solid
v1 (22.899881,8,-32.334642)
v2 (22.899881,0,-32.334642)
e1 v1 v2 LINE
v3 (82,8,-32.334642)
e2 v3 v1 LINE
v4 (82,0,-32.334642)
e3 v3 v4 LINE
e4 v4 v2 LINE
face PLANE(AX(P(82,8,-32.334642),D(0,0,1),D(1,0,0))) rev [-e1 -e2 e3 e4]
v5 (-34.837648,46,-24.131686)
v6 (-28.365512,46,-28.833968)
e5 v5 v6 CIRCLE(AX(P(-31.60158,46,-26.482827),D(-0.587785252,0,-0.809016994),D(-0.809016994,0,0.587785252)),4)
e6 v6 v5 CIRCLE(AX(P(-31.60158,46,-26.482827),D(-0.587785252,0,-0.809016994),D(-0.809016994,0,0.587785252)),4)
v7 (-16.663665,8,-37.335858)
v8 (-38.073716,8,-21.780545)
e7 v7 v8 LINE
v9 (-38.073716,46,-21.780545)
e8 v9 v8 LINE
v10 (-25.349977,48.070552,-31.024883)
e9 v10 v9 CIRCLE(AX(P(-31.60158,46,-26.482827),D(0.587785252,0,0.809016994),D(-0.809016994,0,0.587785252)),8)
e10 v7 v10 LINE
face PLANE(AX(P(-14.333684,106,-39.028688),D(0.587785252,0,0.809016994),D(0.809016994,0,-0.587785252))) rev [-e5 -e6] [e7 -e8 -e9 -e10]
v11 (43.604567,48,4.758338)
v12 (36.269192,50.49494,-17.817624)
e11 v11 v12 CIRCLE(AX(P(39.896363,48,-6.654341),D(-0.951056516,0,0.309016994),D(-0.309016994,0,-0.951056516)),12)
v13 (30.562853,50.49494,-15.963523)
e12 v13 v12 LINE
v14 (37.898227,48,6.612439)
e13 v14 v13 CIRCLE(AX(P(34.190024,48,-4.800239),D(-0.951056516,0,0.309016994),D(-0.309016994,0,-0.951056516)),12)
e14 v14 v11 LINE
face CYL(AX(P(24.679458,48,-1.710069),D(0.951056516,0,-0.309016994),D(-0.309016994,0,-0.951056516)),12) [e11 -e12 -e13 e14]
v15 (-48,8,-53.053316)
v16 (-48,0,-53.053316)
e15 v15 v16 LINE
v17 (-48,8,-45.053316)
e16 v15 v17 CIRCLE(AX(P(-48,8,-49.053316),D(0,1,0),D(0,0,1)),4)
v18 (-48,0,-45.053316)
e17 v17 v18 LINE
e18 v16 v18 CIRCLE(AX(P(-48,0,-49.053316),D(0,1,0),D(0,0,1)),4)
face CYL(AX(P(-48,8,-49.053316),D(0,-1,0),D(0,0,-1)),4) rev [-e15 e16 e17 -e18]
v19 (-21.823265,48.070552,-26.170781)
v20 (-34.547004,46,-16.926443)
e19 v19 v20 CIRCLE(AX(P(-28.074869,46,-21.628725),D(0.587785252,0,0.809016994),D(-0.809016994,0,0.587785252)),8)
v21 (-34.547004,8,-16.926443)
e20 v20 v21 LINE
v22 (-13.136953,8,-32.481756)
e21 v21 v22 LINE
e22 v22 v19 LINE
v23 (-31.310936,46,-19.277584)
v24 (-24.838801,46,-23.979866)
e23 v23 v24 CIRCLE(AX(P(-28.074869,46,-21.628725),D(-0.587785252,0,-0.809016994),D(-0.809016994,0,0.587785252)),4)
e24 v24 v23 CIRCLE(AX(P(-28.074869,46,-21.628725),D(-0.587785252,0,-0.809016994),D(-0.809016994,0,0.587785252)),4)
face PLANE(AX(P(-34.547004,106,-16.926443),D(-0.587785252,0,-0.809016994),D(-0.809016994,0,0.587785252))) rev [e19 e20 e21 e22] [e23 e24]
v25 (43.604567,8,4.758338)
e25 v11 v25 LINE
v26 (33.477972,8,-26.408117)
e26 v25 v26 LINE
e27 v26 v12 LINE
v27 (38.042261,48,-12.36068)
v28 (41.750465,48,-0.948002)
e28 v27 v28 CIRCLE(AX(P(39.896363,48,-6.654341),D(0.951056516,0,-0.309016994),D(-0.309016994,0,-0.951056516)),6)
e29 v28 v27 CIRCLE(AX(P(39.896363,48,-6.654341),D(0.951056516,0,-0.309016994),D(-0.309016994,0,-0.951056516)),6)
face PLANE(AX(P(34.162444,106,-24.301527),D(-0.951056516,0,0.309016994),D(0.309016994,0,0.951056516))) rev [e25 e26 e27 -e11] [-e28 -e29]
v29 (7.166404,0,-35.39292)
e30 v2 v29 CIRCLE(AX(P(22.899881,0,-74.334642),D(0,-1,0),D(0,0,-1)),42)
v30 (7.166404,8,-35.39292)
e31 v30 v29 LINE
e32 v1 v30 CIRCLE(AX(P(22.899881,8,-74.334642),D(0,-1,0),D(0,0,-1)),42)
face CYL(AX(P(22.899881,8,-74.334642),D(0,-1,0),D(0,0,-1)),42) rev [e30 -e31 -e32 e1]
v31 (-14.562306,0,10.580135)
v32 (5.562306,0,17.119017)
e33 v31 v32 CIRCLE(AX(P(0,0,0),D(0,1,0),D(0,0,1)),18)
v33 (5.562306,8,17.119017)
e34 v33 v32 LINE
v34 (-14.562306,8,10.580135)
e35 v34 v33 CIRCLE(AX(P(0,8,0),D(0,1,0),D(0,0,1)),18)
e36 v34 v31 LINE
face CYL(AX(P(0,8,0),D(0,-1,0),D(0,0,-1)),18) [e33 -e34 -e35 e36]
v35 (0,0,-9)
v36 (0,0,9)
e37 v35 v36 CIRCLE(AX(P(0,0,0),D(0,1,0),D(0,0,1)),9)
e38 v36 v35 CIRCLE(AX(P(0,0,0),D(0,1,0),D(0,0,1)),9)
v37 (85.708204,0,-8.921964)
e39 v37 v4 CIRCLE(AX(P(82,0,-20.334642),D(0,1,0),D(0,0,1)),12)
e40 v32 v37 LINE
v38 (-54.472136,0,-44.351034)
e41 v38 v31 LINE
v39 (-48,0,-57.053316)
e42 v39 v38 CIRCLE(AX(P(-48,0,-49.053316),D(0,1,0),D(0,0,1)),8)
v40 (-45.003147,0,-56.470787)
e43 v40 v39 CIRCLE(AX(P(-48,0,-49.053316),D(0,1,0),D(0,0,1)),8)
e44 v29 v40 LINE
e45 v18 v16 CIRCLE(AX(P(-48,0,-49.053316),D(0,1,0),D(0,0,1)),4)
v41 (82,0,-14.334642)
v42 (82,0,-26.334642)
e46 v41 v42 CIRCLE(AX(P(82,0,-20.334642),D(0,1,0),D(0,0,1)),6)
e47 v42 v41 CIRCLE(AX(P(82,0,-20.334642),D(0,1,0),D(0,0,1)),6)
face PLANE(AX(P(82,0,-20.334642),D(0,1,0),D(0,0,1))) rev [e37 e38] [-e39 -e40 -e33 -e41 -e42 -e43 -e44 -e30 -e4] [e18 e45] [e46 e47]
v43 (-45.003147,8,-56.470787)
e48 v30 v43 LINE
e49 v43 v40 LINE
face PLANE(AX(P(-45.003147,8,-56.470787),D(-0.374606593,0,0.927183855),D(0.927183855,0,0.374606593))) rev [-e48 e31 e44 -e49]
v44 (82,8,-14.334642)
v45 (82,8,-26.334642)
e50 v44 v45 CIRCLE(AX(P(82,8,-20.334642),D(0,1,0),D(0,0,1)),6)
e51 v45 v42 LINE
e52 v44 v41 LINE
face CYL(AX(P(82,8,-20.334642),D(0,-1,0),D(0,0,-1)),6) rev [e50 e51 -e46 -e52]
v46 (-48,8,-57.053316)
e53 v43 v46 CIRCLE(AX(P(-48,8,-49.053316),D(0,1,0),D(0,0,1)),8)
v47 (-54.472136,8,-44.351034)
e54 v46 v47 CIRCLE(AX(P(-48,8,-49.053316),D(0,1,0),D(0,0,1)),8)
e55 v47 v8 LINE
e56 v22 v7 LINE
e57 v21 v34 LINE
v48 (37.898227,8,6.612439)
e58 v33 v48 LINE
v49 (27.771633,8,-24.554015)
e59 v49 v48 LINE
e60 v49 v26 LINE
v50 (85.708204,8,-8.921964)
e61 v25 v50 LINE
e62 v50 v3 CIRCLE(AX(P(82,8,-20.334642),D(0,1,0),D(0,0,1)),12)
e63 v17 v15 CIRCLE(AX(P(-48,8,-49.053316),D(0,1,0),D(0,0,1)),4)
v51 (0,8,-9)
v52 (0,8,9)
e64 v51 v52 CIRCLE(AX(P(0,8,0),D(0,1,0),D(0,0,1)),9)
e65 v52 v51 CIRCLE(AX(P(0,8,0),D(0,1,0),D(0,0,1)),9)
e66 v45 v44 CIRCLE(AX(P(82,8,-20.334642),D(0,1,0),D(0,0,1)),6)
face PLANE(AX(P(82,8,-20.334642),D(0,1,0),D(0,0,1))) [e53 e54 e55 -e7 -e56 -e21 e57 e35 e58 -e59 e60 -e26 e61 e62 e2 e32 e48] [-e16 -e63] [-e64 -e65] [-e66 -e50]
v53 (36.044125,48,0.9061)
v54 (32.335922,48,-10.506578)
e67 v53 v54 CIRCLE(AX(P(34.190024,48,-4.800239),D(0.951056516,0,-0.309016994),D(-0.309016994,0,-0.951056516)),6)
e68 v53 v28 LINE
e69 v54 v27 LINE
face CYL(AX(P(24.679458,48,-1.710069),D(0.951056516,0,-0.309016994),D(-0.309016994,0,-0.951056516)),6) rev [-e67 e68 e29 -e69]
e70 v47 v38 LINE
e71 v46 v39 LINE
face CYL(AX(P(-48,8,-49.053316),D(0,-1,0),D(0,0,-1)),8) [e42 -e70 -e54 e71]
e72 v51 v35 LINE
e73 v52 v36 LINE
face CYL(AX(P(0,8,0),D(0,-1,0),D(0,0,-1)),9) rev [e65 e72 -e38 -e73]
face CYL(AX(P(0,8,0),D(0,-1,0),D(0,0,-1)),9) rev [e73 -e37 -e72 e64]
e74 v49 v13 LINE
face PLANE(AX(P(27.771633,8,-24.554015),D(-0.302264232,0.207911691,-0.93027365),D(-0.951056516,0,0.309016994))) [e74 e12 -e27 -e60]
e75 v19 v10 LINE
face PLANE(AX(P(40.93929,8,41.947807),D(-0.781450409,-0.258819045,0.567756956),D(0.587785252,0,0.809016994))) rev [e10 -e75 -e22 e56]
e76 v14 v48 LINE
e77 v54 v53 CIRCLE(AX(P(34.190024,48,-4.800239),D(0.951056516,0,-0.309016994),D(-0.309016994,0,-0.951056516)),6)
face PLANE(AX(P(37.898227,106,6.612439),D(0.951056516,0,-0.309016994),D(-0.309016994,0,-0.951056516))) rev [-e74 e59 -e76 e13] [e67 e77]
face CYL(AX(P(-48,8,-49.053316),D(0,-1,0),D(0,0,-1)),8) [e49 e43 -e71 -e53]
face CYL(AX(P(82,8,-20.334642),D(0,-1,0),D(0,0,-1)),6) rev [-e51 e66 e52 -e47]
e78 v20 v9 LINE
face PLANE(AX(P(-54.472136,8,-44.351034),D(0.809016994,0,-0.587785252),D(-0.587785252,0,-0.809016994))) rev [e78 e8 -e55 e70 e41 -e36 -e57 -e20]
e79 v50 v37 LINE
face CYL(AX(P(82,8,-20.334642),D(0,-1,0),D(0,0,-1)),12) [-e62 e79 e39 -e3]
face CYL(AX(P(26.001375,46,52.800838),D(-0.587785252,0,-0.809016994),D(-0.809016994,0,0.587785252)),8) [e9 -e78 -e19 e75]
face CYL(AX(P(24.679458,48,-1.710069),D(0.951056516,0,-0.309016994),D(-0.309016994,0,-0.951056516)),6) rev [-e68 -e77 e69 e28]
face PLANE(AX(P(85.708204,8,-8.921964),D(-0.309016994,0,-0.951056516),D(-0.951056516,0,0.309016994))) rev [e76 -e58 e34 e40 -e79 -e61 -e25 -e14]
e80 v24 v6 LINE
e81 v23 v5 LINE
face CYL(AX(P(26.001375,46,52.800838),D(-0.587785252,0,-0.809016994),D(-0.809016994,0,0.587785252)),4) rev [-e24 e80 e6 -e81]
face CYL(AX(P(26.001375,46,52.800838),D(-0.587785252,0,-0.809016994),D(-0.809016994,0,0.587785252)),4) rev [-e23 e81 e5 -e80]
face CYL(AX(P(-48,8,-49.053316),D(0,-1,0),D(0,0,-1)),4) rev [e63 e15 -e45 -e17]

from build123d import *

# Parameters (mm, degrees)
BASE_PLATE_SKETCH_R      = 9
BASE_PLATE_SKETCH_R_2    = 6
BASE_PLATE_SKETCH_R_3    = 4
BASE_PLATE_DEPTH         = 8
UPRIGHT_WEB_DEPTH        = 98
WEB_ANGLED_TRIM_SKETCH_R = 4
WEB_ANGLED_TRIM_DEPTH    = 98
PIVOT_LUG_SKETCH_R       = 6
PIVOT_LUG_DEPTH          = 6
LUG_CUT_SKETCH_R         = 6
LUG_CUT_DEPTH            = 16


with BuildPart() as part:
    # Base Plate Sketch → Base Plate (new body)
    with BuildSketch(Plane(origin=(0, 0, 0), x_dir=(1, 0, 0), z_dir=(0, 1, 0))):
        with BuildLine():
            Line((82, 32.334641746), (22.899881176, 32.334641746))
            ThreePointArc((22.899881176, 32.334641746), (14.88590337, 33.106300041), (7.166404253, 35.392919854))
            Line((7.166404253, 35.392919854), (-45.003147253, 56.470786852))
            ThreePointArc((-45.003147253, 56.470786852), (-54.304086029, 53.978607818), (-54.472135955, 44.351033997))
            Line((-54.472135955, 44.351033997), (-14.562305899, -10.580134541))
            ThreePointArc((-14.562305899, -10.580134541), (-5.562305899, -17.119017293), (5.562305899, -17.119017293))
            Line((5.562305899, -17.119017293), (85.708203932, 8.92196355))
            ThreePointArc((85.708203932, 8.92196355), (93.852260087, 22.211855326), (82, 32.334641746))
        make_face()
        with Locations(Location((0, 0, 0), (0, 0, 270))):
            Circle(BASE_PLATE_SKETCH_R, mode=Mode.SUBTRACT)
        with Locations(Location((82, 20.334641746, 0), (0, 0, 270))):
            Circle(BASE_PLATE_SKETCH_R_2, mode=Mode.SUBTRACT)
        with Locations(Location((-48, 49.053316016, 0), (0, 0, 270))):
            Circle(BASE_PLATE_SKETCH_R_3, mode=Mode.SUBTRACT)
    extrude(amount=BASE_PLATE_DEPTH)

    # Upright Web Sketch → Upright Web (add)
    with BuildSketch(Plane(origin=(0, 8, 0), x_dir=(1, 0, 0), z_dir=(0, 1, 0))):
        Polygon((-34.547004477, 16.926443267), (-10.806972302, 34.174586259), (-14.333683815, 39.028688225), (-38.07371599, 21.780545234), align=None)
        Polygon((37.898227453, -6.612439485), (28.456105239, 22.447424608), (34.162444337, 24.301526574), (43.604566551, -4.758337518), align=None)
    extrude(amount=UPRIGHT_WEB_DEPTH)

    # Web Angled Trim Sketch → Web Angled Trim (cut)
    with BuildSketch(Plane(origin=(-23.511410092, 0, -32.360679775), x_dir=(-0.8090169943749421, 0, 0.5877852522924805), z_dir=(-0.5877852522924805, 0, -0.8090169943749422))):
        with Locations((10, 46)):
            Circle(WEB_ANGLED_TRIM_SKETCH_R)
        with BuildLine():
            Line((-8.464278756, 8), (2.27259339, 48.070552361))
            ThreePointArc((2.27259339, 48.070552361), (11.044209538, 53.931558891), (18, 46))
            Line((18, 46), (24.045319571, 43.356543138))
            Line((24.045319571, 43.356543138), (48.419235534, 110.549500658))
            Line((48.419235534, 110.549500658), (-18.279656122, 110.549500658))
            Line((-18.279656122, 110.549500658), (-16.138704045, 8))
            Line((-16.138704045, 8), (-8.464278756, 8))
        make_face()
    extrude(amount=-WEB_ANGLED_TRIM_DEPTH, mode=Mode.SUBTRACT)

    # Pivot Lug Sketch → Pivot Lug (add)
    with BuildSketch(Plane(origin=(38.042260652, 0, -12.360679775), x_dir=(-0.3090169943749489, 0, -0.9510565162951532), z_dir=(0.9510565162951532, 0, -0.3090169943749489))):
        with BuildLine():
            Line((14.770349605, 8), (5.737771209, 50.49494029))
            ThreePointArc((5.737771209, 50.49494029), (-7.254341559, 59.934262744), (-18, 48))
            Line((-18, 48), (-18, 8))
            Line((-18, 8), (14.770349605, 8))
        make_face()
        with Locations((-6, 48)):
            Circle(PIVOT_LUG_SKETCH_R, mode=Mode.SUBTRACT)
    extrude(amount=-PIVOT_LUG_DEPTH)

    # Lug Cut Sketch → Lug Cut (cut)
    with BuildSketch(Plane(origin=(38.042260652, 0, -12.360679775), x_dir=(-0.3090169943749489, 0, -0.9510565162951532), z_dir=(0.9510565162951532, 0, -0.3090169943749489))):
        with Locations((-6, 48)):
            Circle(LUG_CUT_SKETCH_R)
        with BuildLine():
            Line((12.555349334, 18.420756966), (5.737771209, 50.49494029))
            ThreePointArc((5.737771209, 50.49494029), (-7.254341559, 59.934262744), (-18, 48))
            Line((-18, 48), (-46.797997281, 119.82194568))
            Line((-46.797997281, 119.82194568), (32.722077442, 114.455560269))
            Line((32.722077442, 114.455560269), (12.555349334, 18.420756966))
        make_face()
    extrude(amount=-LUG_CUT_DEPTH, mode=Mode.SUBTRACT)


solid = part.part
